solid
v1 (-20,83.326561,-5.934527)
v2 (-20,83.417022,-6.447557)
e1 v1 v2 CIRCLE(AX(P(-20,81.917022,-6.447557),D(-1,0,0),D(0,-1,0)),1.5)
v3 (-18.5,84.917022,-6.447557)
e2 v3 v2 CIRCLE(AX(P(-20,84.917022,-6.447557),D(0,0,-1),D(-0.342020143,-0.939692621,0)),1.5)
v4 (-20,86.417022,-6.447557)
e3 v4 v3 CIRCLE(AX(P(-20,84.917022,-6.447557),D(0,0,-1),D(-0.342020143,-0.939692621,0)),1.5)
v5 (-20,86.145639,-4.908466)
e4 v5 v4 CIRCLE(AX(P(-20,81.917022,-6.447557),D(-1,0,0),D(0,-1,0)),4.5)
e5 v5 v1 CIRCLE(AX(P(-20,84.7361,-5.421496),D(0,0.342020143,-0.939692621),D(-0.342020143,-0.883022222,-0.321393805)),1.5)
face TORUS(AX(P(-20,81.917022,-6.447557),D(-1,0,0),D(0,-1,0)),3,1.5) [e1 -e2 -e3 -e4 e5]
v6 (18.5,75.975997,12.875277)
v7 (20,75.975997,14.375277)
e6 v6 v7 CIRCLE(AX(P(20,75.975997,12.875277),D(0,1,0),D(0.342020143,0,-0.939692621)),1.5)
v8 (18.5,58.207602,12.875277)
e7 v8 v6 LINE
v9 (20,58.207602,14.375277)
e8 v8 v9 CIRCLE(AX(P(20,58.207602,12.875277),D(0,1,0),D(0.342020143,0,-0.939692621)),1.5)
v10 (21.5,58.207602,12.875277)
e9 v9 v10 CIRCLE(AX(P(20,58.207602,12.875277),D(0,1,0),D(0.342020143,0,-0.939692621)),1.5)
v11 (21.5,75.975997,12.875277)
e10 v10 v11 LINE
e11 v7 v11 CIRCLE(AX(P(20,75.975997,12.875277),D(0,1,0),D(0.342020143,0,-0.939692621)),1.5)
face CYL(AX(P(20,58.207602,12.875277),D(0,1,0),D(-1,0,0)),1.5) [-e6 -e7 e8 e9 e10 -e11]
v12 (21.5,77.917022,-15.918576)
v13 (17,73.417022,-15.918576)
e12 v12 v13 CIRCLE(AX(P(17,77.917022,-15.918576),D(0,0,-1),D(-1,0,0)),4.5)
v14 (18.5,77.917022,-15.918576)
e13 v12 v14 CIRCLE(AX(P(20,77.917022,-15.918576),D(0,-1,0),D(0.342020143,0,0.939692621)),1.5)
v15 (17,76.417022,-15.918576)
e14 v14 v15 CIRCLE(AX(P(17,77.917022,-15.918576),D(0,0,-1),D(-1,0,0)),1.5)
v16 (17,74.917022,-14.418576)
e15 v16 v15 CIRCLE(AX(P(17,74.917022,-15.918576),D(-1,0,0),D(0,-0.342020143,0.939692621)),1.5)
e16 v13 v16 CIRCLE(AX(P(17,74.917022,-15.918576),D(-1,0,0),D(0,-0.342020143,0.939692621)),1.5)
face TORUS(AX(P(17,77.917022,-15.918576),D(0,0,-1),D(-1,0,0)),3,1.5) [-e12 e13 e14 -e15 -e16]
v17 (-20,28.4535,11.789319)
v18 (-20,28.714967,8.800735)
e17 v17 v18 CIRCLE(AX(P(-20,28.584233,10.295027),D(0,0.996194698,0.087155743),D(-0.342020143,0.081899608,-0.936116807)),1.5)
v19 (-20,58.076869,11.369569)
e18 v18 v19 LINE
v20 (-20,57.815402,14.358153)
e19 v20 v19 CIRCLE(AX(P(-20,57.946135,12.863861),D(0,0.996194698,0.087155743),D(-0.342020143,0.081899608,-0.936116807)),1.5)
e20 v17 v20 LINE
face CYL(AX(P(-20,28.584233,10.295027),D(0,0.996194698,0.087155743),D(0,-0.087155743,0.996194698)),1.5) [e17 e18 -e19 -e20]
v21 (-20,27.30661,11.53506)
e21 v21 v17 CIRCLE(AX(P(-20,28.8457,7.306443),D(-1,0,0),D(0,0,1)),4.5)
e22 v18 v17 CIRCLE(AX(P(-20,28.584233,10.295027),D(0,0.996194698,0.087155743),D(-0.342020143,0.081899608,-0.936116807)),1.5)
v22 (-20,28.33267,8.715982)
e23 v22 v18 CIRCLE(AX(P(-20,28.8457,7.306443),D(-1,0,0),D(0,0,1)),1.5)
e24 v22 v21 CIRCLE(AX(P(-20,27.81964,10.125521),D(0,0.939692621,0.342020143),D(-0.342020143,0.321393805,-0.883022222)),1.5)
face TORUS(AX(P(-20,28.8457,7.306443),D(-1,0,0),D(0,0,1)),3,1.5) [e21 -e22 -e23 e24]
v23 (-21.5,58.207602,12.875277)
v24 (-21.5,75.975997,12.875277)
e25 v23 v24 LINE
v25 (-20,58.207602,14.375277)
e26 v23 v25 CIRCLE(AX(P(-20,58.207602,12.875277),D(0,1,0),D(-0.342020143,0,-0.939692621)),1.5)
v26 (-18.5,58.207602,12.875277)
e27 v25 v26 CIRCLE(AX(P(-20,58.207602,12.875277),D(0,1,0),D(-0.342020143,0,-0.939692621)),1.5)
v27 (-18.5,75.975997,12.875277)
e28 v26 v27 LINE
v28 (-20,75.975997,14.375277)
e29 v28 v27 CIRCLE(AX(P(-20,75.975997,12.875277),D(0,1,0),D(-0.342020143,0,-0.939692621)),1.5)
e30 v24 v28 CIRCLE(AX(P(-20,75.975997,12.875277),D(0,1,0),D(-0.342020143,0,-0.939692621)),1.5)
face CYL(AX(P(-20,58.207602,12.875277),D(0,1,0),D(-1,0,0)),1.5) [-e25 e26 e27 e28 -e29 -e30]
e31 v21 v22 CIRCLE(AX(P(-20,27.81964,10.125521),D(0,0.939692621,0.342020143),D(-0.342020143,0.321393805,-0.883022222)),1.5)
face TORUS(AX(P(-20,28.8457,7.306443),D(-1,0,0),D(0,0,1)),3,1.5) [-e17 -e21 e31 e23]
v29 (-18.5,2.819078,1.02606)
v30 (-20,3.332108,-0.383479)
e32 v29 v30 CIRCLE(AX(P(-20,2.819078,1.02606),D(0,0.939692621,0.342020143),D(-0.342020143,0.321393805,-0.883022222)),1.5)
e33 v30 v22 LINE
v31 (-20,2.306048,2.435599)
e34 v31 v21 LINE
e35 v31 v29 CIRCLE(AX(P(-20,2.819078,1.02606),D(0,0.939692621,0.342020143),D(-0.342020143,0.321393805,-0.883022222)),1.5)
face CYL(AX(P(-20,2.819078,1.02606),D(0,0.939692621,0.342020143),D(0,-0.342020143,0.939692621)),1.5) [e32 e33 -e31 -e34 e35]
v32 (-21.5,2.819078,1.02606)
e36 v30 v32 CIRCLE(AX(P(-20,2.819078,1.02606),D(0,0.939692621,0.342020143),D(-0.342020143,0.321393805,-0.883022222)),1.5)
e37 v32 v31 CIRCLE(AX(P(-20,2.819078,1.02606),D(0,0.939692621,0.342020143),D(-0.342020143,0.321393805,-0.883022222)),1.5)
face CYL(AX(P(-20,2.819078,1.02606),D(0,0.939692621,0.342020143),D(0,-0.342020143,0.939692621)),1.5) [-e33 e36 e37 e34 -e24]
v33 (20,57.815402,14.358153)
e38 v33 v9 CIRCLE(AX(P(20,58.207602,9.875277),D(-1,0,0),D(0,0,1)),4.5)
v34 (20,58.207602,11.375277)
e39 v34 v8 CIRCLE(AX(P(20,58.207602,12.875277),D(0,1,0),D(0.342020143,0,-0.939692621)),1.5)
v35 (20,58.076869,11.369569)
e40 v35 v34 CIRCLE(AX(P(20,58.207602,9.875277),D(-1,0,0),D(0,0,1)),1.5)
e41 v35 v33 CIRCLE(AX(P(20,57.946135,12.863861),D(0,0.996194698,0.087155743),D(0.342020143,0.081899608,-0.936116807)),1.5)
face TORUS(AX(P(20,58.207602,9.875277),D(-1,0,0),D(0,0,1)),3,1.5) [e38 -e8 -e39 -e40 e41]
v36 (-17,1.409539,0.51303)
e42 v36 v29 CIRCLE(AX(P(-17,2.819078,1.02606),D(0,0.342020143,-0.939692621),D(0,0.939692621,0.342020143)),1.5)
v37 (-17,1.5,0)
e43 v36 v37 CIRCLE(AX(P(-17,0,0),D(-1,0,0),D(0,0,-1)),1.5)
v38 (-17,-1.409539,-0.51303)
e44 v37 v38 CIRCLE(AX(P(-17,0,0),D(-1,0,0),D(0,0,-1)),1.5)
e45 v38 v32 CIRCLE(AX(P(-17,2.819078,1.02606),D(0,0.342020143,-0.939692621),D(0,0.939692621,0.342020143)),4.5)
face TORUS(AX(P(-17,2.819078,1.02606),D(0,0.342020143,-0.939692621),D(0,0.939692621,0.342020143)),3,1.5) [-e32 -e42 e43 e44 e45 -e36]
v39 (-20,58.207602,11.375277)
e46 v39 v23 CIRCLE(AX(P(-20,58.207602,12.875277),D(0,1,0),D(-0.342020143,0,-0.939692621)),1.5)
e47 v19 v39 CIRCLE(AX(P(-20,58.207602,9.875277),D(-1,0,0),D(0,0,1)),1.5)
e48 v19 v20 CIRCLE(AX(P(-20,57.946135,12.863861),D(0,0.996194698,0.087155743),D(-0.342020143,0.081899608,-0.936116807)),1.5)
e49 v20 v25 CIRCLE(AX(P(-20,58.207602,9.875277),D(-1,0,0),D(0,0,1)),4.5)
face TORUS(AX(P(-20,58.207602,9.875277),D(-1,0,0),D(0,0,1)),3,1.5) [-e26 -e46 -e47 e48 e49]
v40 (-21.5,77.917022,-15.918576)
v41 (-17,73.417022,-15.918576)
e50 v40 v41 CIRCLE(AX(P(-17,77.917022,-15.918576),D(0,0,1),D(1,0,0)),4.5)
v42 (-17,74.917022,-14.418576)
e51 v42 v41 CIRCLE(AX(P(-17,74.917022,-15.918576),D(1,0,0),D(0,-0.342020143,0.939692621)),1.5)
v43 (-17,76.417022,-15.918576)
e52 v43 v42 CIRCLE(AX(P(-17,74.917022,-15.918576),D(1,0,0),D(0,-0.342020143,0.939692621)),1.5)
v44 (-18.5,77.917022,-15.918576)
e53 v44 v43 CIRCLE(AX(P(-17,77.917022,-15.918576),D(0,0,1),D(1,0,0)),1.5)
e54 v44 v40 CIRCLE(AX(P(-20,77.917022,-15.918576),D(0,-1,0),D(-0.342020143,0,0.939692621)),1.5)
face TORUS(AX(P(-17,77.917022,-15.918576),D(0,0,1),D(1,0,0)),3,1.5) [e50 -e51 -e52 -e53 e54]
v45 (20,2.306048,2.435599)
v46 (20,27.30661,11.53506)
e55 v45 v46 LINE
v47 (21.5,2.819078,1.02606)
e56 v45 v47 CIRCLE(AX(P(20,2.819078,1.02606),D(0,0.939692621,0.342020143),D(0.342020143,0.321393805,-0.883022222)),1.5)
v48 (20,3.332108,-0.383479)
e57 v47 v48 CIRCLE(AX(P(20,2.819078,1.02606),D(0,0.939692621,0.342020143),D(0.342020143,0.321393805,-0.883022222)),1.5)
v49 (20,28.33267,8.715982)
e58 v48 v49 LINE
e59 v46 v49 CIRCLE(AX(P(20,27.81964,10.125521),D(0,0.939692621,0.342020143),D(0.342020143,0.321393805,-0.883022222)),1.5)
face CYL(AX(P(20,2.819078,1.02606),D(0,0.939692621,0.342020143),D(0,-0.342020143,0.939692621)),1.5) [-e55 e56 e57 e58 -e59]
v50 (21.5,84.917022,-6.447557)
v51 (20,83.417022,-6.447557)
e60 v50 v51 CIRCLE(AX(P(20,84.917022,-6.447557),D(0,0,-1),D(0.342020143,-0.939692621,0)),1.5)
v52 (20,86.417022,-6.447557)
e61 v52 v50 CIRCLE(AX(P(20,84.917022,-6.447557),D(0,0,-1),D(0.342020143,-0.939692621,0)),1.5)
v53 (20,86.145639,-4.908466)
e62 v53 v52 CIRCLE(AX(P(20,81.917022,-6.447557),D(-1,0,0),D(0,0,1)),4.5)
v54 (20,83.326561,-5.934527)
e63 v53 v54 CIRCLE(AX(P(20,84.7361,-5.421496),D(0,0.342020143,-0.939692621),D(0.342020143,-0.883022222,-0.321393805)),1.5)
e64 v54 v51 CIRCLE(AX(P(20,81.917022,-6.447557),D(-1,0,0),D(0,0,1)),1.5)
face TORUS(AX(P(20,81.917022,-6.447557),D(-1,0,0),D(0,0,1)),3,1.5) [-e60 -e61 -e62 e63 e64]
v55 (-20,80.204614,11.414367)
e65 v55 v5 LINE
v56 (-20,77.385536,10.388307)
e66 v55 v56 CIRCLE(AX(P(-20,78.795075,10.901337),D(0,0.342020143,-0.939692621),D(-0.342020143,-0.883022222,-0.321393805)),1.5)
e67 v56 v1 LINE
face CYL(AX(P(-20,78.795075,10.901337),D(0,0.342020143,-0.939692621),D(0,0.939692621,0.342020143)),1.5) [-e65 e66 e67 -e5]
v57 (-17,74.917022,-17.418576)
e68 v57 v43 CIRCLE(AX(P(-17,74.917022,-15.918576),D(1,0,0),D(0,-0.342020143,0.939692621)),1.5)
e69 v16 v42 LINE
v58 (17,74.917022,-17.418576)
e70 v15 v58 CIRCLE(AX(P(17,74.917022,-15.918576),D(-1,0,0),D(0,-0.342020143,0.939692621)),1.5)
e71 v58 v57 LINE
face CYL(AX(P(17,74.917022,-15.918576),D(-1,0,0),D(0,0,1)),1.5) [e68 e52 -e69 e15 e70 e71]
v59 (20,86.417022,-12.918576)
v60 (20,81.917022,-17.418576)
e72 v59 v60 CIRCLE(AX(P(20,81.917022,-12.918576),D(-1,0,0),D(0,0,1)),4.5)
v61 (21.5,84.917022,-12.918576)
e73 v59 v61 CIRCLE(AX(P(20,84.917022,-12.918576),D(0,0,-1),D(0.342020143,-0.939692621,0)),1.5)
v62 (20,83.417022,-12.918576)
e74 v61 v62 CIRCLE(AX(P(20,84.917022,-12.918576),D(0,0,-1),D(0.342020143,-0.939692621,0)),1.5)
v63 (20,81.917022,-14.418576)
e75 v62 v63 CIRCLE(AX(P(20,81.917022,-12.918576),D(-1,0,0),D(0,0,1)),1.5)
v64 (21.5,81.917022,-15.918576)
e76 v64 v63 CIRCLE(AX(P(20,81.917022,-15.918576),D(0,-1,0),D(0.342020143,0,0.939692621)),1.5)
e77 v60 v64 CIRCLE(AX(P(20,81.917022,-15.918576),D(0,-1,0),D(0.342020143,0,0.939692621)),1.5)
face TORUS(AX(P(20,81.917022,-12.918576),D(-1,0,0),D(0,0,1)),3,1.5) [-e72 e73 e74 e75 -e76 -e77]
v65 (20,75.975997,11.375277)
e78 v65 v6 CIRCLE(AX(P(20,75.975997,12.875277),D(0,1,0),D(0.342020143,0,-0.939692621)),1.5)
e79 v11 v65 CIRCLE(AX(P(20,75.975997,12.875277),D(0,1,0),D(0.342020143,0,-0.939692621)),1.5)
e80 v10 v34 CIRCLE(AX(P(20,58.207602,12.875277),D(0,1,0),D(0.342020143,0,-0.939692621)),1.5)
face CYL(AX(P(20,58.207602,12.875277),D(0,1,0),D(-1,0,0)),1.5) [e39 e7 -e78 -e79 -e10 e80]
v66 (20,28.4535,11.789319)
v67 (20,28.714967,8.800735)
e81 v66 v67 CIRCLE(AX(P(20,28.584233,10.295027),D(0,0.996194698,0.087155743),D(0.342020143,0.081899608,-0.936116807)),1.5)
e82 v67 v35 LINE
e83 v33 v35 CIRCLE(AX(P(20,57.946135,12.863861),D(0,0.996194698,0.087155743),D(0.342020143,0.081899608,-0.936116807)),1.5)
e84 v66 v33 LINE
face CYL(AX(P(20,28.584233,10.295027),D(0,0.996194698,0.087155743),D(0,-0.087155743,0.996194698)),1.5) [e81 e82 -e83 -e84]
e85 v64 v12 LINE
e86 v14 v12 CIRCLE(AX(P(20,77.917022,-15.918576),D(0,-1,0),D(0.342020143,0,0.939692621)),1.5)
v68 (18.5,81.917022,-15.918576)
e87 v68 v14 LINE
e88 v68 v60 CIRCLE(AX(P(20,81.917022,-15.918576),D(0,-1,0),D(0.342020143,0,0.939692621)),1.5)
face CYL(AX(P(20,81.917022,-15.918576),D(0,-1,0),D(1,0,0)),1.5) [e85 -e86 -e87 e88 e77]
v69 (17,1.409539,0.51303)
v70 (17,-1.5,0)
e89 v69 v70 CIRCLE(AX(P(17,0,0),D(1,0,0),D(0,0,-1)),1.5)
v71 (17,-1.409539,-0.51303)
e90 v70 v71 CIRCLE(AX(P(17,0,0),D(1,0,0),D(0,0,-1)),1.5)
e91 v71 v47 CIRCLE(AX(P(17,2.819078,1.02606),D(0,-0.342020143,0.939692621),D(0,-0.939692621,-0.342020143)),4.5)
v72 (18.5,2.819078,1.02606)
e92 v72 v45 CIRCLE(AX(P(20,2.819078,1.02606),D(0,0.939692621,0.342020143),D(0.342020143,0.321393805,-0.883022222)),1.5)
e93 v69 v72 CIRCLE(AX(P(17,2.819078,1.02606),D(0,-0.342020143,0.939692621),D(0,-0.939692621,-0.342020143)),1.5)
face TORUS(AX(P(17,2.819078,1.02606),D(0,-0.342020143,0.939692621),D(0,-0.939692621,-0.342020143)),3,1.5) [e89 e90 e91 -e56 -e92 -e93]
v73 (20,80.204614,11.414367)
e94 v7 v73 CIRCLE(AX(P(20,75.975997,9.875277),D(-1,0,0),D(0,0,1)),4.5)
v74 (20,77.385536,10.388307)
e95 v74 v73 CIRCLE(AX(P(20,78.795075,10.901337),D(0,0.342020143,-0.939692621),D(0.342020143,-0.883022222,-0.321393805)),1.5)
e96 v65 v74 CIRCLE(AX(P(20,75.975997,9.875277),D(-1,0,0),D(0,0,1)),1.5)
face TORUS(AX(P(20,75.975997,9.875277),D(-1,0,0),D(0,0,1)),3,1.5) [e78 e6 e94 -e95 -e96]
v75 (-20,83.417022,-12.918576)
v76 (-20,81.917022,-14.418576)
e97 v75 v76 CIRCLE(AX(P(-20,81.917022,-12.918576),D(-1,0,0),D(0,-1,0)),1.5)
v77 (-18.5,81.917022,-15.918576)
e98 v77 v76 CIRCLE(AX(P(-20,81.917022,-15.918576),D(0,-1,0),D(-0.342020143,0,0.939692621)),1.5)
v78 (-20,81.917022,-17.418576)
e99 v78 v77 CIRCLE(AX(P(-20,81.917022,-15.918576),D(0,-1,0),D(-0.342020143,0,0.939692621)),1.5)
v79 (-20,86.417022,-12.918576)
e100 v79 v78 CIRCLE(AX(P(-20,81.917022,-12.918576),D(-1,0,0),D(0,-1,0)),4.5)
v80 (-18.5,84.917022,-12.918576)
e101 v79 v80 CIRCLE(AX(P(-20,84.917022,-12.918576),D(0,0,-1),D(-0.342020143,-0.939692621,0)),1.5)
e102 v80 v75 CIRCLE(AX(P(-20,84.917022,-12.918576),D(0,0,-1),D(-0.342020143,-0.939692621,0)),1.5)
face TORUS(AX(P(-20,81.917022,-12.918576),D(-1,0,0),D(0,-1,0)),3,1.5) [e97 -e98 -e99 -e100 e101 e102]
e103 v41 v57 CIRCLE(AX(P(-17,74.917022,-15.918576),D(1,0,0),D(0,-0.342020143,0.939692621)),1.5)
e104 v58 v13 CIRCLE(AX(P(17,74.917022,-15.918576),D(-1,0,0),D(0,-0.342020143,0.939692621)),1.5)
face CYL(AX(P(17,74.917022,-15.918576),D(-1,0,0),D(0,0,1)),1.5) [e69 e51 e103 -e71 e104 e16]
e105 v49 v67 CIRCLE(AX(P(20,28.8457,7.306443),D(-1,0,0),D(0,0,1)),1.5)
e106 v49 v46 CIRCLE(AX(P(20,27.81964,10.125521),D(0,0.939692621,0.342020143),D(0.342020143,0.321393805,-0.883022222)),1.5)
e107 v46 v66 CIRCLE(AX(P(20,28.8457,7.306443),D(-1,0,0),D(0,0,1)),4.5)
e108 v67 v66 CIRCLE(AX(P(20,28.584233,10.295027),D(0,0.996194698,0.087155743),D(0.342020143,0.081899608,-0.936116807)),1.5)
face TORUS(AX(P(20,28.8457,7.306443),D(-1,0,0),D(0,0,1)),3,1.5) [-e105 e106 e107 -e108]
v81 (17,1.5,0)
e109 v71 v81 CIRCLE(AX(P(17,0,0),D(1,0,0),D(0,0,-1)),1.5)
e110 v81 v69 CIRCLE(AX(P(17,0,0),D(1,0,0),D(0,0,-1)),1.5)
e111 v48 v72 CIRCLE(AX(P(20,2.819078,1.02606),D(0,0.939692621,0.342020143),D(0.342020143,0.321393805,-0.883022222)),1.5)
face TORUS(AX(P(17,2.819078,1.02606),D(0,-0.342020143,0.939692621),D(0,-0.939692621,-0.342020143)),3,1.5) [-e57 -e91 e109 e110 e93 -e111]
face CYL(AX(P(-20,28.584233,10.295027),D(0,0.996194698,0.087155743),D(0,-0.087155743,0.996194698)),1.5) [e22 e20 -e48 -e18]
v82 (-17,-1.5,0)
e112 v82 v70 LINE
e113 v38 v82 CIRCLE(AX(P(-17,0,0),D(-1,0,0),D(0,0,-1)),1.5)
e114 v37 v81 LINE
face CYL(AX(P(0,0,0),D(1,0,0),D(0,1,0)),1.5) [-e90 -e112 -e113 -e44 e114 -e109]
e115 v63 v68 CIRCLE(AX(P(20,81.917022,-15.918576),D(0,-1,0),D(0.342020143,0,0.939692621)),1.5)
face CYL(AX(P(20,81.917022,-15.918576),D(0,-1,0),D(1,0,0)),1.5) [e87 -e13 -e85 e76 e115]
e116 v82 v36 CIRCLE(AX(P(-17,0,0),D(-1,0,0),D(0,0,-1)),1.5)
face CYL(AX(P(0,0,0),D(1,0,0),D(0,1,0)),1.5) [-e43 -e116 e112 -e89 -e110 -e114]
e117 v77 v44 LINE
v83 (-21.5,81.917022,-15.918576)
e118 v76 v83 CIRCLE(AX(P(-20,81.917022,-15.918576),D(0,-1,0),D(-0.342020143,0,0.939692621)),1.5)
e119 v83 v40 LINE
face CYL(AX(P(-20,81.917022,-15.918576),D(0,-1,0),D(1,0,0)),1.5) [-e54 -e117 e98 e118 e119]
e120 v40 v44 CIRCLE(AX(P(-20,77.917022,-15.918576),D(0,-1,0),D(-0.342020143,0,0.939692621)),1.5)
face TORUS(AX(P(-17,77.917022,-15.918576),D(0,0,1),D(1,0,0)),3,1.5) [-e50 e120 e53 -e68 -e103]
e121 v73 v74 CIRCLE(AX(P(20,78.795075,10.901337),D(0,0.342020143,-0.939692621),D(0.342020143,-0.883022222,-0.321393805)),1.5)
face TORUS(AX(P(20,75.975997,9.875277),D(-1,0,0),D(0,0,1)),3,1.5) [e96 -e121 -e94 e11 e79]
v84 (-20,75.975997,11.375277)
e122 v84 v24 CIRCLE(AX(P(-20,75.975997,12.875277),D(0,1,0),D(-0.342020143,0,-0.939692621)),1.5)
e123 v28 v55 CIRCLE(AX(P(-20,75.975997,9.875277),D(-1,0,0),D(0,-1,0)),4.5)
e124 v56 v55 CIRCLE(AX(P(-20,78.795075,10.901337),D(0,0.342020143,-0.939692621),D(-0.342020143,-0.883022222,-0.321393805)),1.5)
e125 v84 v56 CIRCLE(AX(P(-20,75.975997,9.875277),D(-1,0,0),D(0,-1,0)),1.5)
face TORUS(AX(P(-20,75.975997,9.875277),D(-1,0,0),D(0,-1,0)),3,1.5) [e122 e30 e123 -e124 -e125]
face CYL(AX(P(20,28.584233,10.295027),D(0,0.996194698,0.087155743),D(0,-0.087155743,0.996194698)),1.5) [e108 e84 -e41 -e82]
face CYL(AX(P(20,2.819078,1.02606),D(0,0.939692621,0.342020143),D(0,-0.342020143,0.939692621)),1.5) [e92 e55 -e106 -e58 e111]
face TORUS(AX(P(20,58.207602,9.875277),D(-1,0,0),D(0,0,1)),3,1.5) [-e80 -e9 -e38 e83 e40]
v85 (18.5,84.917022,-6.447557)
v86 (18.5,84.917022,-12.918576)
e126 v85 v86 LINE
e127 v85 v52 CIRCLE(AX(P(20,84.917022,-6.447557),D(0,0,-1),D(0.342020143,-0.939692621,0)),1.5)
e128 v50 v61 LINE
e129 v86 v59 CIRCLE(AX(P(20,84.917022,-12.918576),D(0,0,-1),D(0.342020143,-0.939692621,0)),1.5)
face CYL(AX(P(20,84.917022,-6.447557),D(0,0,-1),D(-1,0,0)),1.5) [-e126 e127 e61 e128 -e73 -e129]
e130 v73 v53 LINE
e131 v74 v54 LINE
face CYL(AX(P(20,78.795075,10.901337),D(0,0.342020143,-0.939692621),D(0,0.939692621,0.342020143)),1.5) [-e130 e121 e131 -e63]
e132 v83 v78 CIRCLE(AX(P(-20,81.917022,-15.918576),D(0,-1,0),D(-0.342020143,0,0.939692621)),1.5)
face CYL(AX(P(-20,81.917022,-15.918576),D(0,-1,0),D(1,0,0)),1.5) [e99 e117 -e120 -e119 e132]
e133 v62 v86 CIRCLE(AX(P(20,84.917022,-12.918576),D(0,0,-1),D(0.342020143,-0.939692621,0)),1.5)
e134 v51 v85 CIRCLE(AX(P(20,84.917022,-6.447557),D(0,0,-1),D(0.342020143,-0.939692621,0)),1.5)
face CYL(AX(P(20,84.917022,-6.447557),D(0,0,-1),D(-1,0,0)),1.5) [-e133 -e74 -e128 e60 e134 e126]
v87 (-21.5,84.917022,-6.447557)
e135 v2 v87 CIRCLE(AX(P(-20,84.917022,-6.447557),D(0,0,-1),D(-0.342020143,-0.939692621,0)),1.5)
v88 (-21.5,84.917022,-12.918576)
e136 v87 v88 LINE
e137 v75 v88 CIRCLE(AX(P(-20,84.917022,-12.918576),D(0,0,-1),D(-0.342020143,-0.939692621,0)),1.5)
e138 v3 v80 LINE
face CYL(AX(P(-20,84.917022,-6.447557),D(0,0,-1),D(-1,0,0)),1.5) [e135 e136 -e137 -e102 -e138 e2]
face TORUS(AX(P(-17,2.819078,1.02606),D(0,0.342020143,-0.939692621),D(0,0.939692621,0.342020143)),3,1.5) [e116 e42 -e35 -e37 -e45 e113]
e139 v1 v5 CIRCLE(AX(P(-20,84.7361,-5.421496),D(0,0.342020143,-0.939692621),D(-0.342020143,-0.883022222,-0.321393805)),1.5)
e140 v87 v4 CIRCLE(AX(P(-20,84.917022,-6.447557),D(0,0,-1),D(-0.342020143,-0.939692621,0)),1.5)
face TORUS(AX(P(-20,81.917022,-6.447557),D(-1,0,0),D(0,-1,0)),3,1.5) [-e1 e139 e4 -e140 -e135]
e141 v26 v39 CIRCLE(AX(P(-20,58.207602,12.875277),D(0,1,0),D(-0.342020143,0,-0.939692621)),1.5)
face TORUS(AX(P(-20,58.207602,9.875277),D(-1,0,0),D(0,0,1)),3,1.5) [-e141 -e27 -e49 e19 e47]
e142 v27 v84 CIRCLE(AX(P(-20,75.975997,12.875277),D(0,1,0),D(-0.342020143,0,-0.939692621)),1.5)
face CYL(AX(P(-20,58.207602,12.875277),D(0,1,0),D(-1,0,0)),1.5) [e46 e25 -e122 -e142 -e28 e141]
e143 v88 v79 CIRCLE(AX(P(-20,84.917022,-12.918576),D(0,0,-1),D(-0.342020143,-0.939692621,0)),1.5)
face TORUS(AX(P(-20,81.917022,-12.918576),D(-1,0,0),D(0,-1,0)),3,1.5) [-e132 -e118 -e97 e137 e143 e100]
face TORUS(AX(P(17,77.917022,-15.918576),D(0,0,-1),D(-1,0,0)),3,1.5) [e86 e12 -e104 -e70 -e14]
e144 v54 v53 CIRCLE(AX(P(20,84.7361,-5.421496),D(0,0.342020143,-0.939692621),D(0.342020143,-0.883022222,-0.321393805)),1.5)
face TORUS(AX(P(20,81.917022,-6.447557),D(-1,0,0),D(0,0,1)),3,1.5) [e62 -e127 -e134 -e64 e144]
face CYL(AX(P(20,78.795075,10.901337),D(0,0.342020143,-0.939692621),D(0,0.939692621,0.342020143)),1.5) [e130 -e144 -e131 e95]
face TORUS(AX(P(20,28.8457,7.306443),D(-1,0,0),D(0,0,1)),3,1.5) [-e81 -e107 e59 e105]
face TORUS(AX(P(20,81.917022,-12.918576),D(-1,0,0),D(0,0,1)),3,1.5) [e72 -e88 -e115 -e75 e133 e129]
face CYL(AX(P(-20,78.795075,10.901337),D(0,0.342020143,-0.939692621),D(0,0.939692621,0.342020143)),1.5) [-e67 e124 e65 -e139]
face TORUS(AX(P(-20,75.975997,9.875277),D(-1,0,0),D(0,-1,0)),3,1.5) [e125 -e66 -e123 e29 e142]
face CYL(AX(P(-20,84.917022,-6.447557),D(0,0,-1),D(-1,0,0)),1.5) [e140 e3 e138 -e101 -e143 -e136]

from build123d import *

# Parameters (mm, degrees)
SKETCH1_R = 1.5


with BuildPart() as part:
    # Sweep1: sweep along a curve in space
    with BuildLine() as sweep1_path:
        Line((0, 0, 0), (17, 0, 0))
        ThreePointArc((20, 2.819077862, 1.02606043), (19.121320344, 0.825688789, 0.300526142), (17, 0, 0))
        Line((20, 2.819077862, 1.02606043), (20, 27.819639982, 10.125520881))
        ThreePointArc((20, 28.584233184, 10.295027113), (20, 28.19638157, 10.23533104), (20, 27.819639982, 10.125520881))
        Line((20, 28.584233184, 10.295027113), (20, 57.946135167, 12.863860676))
        ThreePointArc((20, 58.207602395, 12.875276582), (20, 58.076744233, 12.872421247), (20, 57.946135167, 12.863860676))
        Line((20, 58.207602395, 12.875276582), (20, 75.975996952, 12.875276582))
        ThreePointArc((20, 75.975996952, 12.875276582), (20, 77.696726261, 12.332732715), (20, 78.795074814, 10.901337012))
        Line((20, 78.795074814, 10.901337012), (20, 84.736100295, -5.421496346))
        ThreePointArc((20, 84.917022433, -6.447556776), (20, 84.871445692, -5.926612243), (20, 84.736100295, -5.421496346))
        Line((20, 84.917022433, -6.447556776), (20, 84.917022433, -12.918575834))
        ThreePointArc((20, 81.917022433, -15.918575834), (20, 84.038342776, -15.039896177), (20, 84.917022433, -12.918575834))
        Line((20, 81.917022433, -15.918575834), (20, 77.917022433, -15.918575834))
        ThreePointArc((17, 74.917022433, -15.918575834), (19.121320343, 75.795702089, -15.918575834), (20, 77.917022433, -15.918575834))
        Line((17, 74.917022433, -15.918575834), (0, 74.917022433, -15.918575834))
    # Sketch1 → Sweep1 (sweep)
    with BuildSketch(Plane(origin=(0, 0, 0), x_dir=(0, 0, -1), z_dir=(1, 0, 0))):
        Circle(SKETCH1_R)
    sweep1 = sweep(path=sweep1_path.line)

    # Mirror1: Sweep1 across plane
    add(sweep1.mirror(Plane(origin=(0, 74.917022433, -15.918575834), x_dir=(0, 0, 1), z_dir=(-1, 0, 0))))


solid = part.part
